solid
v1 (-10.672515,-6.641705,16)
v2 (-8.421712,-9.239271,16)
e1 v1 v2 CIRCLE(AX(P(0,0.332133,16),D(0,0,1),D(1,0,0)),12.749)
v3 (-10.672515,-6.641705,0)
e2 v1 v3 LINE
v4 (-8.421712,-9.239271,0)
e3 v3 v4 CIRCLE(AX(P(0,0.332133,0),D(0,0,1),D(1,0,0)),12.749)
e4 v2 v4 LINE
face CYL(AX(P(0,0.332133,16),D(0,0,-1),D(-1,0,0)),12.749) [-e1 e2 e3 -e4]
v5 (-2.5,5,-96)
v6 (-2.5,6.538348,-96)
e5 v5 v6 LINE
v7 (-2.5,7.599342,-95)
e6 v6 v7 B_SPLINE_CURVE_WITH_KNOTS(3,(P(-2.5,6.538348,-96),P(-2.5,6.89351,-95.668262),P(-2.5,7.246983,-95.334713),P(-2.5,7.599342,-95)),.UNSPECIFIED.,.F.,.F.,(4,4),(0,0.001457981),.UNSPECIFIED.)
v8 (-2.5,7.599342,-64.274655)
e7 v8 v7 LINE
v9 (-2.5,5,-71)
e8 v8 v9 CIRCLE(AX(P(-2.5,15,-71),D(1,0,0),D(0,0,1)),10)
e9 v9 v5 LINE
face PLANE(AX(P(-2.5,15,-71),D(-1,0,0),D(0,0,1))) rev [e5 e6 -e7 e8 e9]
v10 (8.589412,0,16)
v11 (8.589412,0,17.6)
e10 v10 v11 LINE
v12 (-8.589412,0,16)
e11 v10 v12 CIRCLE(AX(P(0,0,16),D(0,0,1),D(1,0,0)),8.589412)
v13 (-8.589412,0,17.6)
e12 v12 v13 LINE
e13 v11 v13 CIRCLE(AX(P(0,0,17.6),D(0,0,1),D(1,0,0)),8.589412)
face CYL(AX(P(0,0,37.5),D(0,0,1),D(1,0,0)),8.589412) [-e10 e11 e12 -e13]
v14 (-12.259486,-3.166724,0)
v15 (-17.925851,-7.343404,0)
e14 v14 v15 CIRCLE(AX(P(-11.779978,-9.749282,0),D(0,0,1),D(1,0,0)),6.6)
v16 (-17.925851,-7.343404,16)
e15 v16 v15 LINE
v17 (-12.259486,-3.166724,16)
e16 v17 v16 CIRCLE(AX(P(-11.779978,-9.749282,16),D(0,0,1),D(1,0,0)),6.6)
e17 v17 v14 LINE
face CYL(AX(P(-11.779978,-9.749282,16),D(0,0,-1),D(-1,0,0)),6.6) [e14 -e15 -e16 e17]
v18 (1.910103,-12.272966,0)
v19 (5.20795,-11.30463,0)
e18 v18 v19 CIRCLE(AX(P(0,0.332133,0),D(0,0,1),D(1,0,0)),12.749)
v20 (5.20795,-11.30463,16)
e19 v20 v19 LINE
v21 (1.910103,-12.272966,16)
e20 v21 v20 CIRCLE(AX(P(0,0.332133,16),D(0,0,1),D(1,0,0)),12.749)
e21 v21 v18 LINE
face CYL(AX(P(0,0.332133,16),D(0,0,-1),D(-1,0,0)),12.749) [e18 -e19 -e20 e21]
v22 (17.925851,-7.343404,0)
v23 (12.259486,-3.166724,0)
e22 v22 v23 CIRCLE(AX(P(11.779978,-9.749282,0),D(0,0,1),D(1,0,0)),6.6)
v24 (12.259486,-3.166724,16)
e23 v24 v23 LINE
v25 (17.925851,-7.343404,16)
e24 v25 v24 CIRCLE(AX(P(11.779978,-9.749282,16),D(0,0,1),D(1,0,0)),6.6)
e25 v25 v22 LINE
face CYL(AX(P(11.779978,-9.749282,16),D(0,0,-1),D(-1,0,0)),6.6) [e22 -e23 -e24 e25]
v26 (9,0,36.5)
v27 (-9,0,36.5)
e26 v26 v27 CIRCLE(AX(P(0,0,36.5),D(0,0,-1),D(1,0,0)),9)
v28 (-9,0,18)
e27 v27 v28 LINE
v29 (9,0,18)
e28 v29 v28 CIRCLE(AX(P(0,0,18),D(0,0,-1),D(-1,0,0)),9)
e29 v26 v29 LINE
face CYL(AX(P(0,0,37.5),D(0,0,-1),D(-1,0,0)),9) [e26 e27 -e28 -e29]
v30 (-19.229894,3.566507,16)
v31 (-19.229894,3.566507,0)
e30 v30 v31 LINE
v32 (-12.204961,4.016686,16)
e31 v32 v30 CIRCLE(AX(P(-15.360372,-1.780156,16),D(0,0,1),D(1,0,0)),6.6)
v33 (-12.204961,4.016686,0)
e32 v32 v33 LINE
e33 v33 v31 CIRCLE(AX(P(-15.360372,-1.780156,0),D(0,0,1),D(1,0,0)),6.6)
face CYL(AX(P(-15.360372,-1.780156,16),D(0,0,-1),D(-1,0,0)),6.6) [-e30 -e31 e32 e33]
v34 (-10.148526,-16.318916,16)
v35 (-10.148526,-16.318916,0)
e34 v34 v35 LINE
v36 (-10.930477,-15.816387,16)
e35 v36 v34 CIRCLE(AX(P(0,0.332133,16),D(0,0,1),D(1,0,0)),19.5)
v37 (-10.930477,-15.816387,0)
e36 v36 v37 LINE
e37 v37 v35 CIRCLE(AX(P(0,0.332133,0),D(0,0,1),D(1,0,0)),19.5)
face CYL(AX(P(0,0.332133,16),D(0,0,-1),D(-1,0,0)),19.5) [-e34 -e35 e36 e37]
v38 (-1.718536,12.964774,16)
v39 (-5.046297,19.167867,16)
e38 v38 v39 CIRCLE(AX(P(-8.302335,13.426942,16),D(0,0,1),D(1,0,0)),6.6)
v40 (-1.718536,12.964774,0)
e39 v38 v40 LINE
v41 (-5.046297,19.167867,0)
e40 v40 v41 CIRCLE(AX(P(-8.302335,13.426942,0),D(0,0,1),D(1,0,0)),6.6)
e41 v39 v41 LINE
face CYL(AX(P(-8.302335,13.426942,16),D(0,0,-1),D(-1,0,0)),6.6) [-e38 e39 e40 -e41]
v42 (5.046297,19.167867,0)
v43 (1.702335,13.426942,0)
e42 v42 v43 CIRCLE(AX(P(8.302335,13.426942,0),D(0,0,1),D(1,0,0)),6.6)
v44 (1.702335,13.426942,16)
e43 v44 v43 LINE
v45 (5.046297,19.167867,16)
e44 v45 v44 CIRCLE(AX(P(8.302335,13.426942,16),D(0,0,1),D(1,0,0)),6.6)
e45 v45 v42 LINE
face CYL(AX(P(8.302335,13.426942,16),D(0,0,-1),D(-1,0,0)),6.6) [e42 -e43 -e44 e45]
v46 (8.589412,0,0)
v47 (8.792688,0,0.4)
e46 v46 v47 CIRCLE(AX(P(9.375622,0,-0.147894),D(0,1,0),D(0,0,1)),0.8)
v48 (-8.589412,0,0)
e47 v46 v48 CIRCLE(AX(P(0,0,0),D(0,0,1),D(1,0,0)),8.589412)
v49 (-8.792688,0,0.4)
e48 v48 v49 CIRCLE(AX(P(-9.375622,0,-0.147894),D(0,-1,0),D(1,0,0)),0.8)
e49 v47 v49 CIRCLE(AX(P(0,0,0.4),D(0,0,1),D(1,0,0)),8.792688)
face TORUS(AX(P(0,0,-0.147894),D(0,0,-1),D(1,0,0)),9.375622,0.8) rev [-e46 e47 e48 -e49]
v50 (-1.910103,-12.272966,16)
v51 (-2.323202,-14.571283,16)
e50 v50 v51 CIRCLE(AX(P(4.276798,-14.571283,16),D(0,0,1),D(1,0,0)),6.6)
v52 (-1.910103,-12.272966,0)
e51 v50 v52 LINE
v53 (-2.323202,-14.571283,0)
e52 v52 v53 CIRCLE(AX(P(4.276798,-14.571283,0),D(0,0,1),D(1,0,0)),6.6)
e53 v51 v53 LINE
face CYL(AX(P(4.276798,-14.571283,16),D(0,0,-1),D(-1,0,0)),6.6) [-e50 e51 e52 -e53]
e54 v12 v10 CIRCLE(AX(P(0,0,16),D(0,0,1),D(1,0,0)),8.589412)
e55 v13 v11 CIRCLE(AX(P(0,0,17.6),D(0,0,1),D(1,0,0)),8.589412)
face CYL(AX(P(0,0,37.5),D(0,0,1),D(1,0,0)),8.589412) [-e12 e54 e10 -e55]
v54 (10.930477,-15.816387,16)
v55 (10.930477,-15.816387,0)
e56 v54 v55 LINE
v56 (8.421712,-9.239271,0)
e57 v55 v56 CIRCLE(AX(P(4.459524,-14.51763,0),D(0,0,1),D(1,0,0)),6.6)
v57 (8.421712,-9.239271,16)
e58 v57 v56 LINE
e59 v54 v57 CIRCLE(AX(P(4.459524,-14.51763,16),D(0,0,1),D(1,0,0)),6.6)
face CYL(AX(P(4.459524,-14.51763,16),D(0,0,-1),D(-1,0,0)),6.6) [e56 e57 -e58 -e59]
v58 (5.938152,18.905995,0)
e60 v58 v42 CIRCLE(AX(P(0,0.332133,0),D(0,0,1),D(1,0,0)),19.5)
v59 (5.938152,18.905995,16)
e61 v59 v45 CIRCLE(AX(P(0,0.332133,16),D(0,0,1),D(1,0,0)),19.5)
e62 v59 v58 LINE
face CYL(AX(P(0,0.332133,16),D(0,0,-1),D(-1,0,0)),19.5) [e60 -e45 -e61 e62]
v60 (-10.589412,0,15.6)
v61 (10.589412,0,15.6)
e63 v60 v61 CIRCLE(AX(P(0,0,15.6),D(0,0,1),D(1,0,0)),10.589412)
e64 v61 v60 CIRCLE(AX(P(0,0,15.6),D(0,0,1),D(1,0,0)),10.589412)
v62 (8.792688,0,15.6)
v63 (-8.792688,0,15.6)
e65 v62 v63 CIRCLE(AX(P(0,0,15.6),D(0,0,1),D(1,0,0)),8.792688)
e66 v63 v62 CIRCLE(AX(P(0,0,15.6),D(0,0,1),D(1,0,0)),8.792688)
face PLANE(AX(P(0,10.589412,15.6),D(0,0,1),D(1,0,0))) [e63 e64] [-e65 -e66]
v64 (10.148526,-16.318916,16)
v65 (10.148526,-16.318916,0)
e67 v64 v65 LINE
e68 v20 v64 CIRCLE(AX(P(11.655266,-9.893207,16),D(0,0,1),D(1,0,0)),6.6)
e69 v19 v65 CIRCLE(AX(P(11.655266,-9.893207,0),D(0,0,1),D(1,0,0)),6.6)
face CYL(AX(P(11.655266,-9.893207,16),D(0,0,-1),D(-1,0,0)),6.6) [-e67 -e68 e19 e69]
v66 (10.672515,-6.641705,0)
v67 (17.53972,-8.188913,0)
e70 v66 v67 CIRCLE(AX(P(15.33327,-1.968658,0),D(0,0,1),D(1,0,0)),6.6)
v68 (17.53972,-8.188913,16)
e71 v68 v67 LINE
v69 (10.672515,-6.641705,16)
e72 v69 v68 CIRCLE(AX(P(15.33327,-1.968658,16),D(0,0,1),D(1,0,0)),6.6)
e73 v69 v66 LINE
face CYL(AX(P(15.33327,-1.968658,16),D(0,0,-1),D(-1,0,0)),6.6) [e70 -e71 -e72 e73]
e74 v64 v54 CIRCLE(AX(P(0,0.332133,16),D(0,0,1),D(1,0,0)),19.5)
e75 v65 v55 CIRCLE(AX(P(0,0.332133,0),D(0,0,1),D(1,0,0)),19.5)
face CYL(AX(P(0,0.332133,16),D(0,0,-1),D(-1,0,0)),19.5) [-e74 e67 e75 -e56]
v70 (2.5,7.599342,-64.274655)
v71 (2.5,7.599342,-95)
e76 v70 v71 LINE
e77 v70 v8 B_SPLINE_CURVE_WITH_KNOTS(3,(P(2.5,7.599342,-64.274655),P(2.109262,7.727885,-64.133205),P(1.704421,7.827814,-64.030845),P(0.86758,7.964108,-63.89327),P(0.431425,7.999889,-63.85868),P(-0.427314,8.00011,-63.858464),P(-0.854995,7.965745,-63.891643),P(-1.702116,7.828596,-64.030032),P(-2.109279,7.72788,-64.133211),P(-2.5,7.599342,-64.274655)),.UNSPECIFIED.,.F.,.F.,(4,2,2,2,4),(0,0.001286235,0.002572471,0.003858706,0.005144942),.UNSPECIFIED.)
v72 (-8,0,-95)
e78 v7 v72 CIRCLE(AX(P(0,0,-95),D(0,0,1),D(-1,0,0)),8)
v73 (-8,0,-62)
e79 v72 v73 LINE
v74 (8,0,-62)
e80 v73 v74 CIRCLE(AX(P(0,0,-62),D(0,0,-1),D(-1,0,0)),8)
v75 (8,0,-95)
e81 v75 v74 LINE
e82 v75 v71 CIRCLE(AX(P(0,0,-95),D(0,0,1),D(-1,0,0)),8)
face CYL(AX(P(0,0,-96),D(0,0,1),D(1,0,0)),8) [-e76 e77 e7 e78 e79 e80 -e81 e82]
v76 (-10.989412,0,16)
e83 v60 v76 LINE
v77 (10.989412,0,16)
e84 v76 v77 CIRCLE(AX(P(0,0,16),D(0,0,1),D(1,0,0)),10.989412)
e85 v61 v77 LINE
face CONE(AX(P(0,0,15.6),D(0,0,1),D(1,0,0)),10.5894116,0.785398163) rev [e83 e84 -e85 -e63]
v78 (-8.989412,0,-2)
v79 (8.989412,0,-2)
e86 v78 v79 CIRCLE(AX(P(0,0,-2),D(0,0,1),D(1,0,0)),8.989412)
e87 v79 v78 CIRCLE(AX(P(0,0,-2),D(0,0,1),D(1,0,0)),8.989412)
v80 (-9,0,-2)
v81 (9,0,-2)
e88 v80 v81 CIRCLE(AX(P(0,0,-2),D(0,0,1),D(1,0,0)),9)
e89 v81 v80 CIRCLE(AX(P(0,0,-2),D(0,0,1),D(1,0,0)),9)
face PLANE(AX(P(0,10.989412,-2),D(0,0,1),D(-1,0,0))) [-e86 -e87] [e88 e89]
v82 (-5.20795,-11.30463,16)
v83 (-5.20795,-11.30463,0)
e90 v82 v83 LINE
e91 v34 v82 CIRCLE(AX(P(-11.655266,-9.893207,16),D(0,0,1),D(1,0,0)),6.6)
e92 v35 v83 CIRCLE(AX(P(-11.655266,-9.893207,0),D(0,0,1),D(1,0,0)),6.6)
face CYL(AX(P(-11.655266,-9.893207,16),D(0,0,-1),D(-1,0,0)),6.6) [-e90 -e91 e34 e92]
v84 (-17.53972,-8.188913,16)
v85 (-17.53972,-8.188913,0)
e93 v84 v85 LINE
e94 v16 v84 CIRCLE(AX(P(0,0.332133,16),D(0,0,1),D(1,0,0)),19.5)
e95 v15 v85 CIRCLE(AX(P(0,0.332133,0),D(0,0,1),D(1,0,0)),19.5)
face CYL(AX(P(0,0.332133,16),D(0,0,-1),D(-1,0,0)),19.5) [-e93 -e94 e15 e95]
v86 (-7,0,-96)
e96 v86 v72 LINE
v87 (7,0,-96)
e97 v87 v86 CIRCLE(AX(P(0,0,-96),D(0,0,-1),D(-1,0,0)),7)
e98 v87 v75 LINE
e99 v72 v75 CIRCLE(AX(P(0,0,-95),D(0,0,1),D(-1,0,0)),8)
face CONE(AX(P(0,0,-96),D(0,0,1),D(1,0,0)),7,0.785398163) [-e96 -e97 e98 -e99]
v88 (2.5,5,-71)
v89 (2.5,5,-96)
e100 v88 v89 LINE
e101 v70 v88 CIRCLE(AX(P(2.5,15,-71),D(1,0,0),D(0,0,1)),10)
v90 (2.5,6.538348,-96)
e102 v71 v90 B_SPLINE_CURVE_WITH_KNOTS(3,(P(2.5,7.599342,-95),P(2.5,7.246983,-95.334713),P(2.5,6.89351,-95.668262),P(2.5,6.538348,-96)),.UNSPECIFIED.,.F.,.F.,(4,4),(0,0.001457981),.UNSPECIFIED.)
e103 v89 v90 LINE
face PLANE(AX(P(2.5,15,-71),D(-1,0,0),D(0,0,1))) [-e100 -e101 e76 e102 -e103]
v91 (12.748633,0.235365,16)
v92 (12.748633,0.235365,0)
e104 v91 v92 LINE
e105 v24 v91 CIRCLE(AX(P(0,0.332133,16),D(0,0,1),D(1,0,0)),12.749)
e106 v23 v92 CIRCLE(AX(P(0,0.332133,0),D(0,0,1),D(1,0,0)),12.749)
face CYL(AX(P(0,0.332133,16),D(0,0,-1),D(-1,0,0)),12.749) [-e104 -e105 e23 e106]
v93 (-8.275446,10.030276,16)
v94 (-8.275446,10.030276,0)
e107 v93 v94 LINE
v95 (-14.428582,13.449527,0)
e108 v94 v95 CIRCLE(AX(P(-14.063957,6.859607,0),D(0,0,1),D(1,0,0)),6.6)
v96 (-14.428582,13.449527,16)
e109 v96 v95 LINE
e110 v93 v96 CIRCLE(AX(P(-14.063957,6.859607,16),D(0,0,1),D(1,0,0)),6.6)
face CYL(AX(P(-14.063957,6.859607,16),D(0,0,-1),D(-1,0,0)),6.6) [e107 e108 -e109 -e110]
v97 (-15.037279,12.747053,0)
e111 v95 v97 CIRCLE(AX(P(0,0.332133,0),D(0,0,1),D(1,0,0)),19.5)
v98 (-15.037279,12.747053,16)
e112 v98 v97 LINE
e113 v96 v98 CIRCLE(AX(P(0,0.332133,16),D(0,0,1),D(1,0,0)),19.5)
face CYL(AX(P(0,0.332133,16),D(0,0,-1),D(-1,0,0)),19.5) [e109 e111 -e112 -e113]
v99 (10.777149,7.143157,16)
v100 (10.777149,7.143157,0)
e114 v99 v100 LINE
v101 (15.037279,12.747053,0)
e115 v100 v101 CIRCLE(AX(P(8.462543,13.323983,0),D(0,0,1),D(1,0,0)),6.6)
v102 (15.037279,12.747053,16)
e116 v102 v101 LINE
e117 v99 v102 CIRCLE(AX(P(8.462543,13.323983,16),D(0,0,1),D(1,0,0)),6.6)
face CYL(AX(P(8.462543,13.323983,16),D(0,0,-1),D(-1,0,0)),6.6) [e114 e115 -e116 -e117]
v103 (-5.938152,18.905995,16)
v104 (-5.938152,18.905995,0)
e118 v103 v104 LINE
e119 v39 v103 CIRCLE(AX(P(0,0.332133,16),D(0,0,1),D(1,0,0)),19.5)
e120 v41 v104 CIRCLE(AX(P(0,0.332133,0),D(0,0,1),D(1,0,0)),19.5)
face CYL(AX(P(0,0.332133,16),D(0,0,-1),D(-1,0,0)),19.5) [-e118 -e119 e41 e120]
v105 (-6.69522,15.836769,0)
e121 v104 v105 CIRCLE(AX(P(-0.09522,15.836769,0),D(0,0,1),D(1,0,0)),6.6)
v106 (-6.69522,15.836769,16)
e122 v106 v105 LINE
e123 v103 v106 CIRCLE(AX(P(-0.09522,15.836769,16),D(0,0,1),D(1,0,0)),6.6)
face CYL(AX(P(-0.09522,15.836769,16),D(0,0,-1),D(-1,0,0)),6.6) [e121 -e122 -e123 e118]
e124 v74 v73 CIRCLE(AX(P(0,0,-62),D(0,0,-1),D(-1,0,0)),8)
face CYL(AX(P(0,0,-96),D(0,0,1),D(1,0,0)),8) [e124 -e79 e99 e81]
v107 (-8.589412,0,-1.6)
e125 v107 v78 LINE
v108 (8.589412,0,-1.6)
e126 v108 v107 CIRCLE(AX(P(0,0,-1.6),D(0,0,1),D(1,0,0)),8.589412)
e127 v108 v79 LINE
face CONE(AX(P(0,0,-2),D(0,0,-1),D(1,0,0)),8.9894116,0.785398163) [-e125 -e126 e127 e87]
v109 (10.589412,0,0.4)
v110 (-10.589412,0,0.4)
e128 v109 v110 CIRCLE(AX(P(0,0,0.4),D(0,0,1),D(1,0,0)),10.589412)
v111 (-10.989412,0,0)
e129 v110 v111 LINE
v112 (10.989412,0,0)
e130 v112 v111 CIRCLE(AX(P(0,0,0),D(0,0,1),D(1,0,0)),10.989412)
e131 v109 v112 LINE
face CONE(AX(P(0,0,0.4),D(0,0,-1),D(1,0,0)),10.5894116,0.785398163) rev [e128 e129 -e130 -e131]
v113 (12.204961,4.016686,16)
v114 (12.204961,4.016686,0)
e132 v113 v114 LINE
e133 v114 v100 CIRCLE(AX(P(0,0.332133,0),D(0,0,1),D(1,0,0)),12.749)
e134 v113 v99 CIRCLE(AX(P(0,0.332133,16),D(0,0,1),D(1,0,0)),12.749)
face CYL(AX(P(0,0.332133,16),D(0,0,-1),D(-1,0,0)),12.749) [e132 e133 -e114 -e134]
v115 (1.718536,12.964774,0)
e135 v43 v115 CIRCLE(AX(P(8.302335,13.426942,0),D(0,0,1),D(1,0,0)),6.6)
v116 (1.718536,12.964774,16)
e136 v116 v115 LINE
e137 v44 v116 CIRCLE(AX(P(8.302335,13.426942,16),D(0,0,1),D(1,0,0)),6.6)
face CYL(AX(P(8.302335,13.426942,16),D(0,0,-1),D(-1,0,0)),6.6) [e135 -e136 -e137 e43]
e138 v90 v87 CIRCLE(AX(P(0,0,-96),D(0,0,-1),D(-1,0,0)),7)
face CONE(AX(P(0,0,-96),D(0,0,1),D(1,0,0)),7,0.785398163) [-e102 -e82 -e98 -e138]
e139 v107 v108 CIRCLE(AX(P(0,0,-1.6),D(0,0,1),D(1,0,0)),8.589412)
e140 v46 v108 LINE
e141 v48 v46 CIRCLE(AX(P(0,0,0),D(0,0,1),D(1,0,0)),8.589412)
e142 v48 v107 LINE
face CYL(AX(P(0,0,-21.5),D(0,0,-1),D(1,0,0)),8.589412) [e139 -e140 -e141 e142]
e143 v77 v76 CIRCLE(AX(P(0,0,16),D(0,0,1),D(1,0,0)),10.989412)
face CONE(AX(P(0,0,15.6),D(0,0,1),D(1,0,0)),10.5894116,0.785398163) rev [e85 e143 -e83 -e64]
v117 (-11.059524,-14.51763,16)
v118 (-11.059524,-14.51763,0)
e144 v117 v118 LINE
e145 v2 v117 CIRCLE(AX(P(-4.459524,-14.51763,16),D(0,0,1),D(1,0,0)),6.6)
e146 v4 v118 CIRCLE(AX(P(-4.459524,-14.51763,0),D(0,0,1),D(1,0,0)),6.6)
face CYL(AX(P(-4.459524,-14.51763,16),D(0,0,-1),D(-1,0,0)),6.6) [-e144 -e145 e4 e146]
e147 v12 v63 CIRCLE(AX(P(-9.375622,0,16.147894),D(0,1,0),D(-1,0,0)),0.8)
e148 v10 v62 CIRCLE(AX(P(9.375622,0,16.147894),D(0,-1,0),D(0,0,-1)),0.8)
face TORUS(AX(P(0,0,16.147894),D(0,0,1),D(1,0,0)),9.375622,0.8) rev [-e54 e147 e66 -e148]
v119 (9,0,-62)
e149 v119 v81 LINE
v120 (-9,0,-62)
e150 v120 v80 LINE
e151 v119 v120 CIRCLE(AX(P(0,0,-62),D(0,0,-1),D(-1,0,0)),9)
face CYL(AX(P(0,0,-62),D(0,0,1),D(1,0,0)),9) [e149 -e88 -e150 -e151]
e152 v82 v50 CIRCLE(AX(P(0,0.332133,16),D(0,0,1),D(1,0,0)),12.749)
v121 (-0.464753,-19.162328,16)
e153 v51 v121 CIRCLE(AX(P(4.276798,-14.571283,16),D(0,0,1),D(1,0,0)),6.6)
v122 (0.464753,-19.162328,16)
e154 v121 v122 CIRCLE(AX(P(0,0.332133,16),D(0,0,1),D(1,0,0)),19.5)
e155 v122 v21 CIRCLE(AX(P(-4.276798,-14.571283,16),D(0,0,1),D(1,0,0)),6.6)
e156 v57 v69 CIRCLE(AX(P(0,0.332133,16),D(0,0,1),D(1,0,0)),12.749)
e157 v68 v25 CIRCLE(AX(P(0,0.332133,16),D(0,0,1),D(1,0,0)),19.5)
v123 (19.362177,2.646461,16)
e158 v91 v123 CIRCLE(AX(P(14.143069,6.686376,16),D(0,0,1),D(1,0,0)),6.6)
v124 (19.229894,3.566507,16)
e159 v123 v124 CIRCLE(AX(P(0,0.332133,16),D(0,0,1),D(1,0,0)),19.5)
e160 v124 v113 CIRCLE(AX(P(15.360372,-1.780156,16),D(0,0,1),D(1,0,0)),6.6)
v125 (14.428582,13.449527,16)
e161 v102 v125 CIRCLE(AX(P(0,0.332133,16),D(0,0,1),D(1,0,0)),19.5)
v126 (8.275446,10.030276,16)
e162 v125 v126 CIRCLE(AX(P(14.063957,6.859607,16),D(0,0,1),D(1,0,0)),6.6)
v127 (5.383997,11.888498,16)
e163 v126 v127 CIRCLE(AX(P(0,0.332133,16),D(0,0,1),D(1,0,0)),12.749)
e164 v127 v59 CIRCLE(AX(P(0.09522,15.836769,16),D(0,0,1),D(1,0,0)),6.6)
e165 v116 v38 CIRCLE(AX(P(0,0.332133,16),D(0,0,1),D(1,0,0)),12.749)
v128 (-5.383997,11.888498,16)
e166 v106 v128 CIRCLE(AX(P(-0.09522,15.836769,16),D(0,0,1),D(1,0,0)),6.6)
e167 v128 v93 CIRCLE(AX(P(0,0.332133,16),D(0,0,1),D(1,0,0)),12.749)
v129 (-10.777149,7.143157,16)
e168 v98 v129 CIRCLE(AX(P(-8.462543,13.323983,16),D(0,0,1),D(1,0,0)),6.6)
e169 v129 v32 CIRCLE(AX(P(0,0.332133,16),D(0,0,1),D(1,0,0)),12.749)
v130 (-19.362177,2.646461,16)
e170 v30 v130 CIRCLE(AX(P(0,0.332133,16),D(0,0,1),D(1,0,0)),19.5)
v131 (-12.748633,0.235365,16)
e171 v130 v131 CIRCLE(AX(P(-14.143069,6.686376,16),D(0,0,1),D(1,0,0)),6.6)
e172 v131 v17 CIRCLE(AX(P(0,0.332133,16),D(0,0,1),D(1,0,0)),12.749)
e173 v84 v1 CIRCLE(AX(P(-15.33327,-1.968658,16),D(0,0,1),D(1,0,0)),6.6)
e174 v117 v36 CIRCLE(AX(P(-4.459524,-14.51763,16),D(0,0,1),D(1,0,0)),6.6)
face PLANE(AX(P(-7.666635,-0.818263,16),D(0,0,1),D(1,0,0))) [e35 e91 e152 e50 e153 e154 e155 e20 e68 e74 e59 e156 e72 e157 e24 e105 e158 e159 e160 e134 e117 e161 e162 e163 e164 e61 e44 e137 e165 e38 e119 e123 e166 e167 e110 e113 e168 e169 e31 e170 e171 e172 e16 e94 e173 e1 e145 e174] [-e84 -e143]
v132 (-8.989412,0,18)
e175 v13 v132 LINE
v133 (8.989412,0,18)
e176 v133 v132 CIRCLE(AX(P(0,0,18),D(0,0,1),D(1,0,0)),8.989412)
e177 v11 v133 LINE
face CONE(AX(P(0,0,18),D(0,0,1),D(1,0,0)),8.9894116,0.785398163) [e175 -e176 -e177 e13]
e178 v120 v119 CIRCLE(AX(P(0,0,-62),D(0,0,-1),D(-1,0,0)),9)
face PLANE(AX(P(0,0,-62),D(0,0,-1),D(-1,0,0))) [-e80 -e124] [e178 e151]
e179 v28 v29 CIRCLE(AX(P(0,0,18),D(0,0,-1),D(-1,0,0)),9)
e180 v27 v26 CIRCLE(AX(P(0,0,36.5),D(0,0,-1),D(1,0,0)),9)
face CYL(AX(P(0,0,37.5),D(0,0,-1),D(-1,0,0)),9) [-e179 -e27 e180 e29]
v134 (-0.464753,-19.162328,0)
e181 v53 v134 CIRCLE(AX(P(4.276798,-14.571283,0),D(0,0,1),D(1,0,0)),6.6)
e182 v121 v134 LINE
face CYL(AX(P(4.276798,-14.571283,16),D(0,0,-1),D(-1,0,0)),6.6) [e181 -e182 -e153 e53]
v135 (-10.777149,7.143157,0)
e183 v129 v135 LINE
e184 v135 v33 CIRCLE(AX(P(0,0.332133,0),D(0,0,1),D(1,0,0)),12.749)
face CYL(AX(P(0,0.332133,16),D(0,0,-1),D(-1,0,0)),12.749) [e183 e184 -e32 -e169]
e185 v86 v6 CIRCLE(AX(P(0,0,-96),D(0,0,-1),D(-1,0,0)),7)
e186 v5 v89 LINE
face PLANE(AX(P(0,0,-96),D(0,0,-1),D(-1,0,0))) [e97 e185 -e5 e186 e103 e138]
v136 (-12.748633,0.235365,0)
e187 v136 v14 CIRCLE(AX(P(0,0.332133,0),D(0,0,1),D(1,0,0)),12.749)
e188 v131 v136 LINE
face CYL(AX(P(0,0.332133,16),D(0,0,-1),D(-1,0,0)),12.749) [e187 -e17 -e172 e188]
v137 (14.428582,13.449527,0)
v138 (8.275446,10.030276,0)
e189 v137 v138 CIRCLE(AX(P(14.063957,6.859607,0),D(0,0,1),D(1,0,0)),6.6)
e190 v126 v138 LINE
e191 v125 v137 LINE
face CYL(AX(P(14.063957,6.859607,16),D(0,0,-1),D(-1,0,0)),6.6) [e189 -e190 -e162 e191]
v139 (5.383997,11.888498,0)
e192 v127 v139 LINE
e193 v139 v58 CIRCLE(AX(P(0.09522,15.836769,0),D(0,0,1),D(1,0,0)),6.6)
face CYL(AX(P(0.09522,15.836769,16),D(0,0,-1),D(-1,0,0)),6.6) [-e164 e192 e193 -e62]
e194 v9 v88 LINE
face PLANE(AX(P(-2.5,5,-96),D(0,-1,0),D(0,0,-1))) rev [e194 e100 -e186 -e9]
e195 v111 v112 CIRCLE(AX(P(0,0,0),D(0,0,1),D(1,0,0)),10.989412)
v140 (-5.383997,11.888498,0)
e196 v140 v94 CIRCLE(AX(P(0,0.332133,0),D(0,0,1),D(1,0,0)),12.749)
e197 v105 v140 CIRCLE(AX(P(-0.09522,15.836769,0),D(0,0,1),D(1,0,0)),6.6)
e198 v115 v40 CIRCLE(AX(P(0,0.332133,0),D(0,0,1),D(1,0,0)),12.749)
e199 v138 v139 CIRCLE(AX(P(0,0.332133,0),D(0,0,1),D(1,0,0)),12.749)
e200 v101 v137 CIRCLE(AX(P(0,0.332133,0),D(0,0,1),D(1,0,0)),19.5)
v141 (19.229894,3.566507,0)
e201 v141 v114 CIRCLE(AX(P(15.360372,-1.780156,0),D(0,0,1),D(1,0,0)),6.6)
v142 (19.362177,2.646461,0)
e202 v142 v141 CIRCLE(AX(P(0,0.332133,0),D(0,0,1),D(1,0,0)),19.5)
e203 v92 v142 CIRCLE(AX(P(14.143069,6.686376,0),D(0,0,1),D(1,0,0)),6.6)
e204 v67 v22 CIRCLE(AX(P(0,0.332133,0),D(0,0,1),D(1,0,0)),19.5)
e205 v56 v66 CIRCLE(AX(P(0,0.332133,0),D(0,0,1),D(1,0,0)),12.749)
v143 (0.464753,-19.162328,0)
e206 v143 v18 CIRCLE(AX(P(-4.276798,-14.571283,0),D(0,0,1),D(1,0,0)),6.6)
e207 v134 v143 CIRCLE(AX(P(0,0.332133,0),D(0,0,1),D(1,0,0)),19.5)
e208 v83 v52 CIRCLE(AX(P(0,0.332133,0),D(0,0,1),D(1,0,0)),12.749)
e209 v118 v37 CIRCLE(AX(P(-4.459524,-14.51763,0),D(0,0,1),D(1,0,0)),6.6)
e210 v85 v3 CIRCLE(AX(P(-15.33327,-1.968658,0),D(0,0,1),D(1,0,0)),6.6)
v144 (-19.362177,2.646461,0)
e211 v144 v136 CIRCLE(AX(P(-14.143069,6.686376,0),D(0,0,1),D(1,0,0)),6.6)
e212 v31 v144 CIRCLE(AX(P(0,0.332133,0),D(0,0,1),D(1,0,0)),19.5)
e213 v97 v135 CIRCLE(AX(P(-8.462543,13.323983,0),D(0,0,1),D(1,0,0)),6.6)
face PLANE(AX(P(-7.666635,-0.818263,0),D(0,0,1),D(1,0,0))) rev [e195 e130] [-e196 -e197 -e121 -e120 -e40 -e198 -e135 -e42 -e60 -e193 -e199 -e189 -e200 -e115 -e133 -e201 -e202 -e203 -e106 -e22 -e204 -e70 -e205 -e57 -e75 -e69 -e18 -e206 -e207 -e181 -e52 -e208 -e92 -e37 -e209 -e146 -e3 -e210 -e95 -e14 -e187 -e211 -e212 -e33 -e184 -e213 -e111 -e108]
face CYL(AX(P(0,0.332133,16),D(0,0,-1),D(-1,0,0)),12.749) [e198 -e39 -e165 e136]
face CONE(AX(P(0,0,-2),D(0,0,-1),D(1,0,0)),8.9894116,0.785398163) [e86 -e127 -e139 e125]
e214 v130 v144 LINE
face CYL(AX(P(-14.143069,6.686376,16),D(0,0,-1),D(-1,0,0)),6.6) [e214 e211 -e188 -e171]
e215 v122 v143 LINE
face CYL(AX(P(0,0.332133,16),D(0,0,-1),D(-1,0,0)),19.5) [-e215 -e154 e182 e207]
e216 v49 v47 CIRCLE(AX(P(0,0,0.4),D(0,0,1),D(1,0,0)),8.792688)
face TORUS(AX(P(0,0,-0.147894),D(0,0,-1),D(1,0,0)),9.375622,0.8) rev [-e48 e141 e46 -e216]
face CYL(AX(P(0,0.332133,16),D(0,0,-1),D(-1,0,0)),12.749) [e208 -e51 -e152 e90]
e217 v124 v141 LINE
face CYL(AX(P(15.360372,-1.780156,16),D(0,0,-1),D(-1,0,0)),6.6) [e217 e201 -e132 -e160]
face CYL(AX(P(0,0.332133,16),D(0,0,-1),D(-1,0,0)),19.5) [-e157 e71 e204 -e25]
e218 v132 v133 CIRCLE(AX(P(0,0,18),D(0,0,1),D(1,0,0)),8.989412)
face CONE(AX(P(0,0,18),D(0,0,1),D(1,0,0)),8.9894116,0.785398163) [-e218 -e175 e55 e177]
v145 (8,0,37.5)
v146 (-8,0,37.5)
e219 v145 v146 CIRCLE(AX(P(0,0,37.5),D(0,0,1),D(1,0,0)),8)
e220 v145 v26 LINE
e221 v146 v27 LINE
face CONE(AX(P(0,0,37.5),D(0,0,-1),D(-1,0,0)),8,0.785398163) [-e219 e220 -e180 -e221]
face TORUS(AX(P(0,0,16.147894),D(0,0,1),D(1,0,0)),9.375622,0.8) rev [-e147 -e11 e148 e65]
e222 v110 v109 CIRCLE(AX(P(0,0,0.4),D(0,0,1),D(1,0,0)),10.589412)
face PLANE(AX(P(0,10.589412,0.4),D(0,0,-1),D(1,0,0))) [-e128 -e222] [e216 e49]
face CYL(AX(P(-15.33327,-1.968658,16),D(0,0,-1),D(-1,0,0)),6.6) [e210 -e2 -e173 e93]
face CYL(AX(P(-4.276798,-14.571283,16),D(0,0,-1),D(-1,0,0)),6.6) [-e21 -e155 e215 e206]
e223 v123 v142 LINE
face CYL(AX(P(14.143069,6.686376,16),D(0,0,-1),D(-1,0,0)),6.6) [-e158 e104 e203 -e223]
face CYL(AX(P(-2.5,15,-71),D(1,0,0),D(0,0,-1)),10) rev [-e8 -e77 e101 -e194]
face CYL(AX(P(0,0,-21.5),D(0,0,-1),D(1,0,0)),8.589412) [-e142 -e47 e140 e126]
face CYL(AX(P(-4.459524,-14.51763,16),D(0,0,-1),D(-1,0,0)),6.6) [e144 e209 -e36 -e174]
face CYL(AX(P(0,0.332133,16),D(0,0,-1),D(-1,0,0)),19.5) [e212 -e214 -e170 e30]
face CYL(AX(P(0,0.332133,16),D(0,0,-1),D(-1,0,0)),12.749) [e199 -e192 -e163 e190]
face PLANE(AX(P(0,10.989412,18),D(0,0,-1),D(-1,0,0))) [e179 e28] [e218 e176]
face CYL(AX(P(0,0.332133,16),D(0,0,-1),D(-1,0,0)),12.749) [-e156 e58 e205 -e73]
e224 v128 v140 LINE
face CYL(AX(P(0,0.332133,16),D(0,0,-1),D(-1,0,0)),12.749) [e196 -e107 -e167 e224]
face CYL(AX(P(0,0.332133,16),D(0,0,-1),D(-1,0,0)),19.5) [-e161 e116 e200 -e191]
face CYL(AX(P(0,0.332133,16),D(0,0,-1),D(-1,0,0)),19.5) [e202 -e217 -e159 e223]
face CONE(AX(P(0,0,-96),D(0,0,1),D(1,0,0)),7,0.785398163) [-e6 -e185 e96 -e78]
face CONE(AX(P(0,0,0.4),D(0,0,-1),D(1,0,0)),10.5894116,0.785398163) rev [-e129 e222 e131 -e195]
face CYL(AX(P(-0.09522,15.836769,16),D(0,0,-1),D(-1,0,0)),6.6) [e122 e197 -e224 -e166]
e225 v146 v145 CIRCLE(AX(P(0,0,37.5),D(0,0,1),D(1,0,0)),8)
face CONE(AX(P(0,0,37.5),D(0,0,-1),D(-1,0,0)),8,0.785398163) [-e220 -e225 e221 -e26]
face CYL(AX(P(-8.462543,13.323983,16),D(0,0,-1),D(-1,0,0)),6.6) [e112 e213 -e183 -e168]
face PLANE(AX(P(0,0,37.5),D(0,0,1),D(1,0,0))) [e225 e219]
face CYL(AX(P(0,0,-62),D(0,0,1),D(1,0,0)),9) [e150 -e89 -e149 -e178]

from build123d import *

# Parameters (mm, degrees)
EXTRUDE_1_DEPTH     = 16
SKETCH_2_R          = 9
EXTRUDE_2_DEPTH     = 21.5
EXTRUDE_START       = 62
SKETCH_3_R          = 9
EXTRUDE_3_DEPTH     = 62
SKETCH_4_R          = 8
EXTRUDE_4_DEPTH     = 34
CUT_EXTRUDE_1_DEPTH = 2.5
CHAMFER_1_SIZE      = 1


with BuildPart() as part:
    # 草图1 → 凸台-拉伸1 (new body)
    with BuildSketch(Plane.XY):
        with BuildLine():
            ThreePointArc((-17.539719795, -8.188913461), (-13.882626521, -8.407262966), (-10.672515451, -6.641705083))
            ThreePointArc((-10.672515451, -6.641705083), (-9.635051323, -8.016686689), (-8.421711588, -9.239271212))
            ThreePointArc((-8.421711588, -9.239271212), (-10.626145075, -12.165442895), (-10.930476691, -15.816386607))
            ThreePointArc((-10.930476691, -15.816386607), (-10.54249594, -16.072311082), (-10.148525822, -16.318915917))
            ThreePointArc((-10.148525822, -16.318915917), (-6.95393453, -14.525429313), (-5.207949909, -11.304630433))
            ThreePointArc((-5.207949909, -11.304630433), (-3.591808367, -11.900443112), (-1.910102932, -12.272965675))
            ThreePointArc((-1.910102932, -12.272965675), (-2.18258254, -15.926424664), (-0.464753394, -19.162328053))
            ThreePointArc((-0.464753394, -19.162328053), (0, -19.167867192), (0.464753394, -19.162328053))
            ThreePointArc((0.464753394, -19.162328053), (2.18258254, -15.926424664), (1.910102932, -12.272965675))
            ThreePointArc((1.910102932, -12.272965675), (3.591808367, -11.900443112), (5.207949909, -11.304630433))
            ThreePointArc((5.207949909, -11.304630433), (6.95393453, -14.525429313), (10.148525822, -16.318915917))
            ThreePointArc((10.148525822, -16.318915917), (10.54249594, -16.072311082), (10.930476691, -15.816386607))
            ThreePointArc((10.930476691, -15.816386607), (10.626145075, -12.165442895), (8.421711588, -9.239271212))
            ThreePointArc((8.421711588, -9.239271212), (9.635051323, -8.016686689), (10.672515451, -6.641705083))
            ThreePointArc((10.672515451, -6.641705083), (13.882626521, -8.407262966), (17.539719795, -8.188913461))
            ThreePointArc((17.539719795, -8.188913461), (17.737823909, -7.768459945), (17.925850869, -7.343404347))
            ThreePointArc((17.925850869, -7.343404347), (15.69598163, -4.436569144), (12.25948632, -3.166723601))
            ThreePointArc((12.25948632, -3.166723601), (12.619233563, -1.482239065), (12.748632746, 0.235364522))
            ThreePointArc((12.748632746, 0.235364522), (16.403682682, 0.485599789), (19.362176663, 2.646460979))
            ThreePointArc((19.362176663, 2.646460979), (19.301518117, 3.107272155), (19.229894055, 3.566506728))
            ThreePointArc((19.229894055, 3.566506728), (15.782454919, 4.806333783), (12.204960767, 4.016686199))
            ThreePointArc((12.204960767, 4.016686199), (11.596898309, 5.628258809), (10.777149222, 7.143157375))
            ThreePointArc((10.777149222, 7.143157375), (13.716685494, 9.329737862), (15.037279247, 12.747052577))
            ThreePointArc((15.037279247, 12.747052577), (14.7371167, 13.10191712), (14.42858175, 13.449526936))
            ThreePointArc((14.42858175, 13.449526936), (10.858110285, 12.628709513), (8.275446406, 10.030276331))
            ThreePointArc((8.275446406, 10.030276331), (6.892629782, 11.057274099), (5.383996967, 11.888498053))
            ThreePointArc((5.383996967, 11.888498053), (6.674737579, 15.317199905), (5.938151919, 18.905994868))
            ThreePointArc((5.938151919, 18.905994868), (5.493784858, 19.042245794), (5.046296687, 19.167867192))
            ThreePointArc((5.046296687, 19.167867192), (2.486392356, 16.547009024), (1.718536283, 12.964774418))
            ThreePointArc((1.718536283, 12.964774418), (0, 13.081132808), (-1.718536283, 12.964774418))
            ThreePointArc((-1.718536283, 12.964774418), (-2.486392356, 16.547009024), (-5.046296687, 19.167867192))
            ThreePointArc((-5.046296687, 19.167867192), (-5.493784858, 19.042245794), (-5.938151919, 18.905994868))
            ThreePointArc((-5.938151919, 18.905994868), (-6.674737579, 15.317199905), (-5.383996967, 11.888498053))
            ThreePointArc((-5.383996967, 11.888498053), (-6.892629782, 11.057274099), (-8.275446406, 10.030276331))
            ThreePointArc((-8.275446406, 10.030276331), (-10.858110285, 12.628709513), (-14.42858175, 13.449526936))
            ThreePointArc((-14.42858175, 13.449526936), (-14.7371167, 13.10191712), (-15.037279247, 12.747052577))
            ThreePointArc((-15.037279247, 12.747052577), (-13.716685494, 9.329737862), (-10.777149222, 7.143157375))
            ThreePointArc((-10.777149222, 7.143157375), (-11.596898309, 5.628258809), (-12.204960767, 4.016686199))
            ThreePointArc((-12.204960767, 4.016686199), (-15.782454919, 4.806333783), (-19.229894055, 3.566506728))
            ThreePointArc((-19.229894055, 3.566506728), (-19.301518117, 3.107272155), (-19.362176663, 2.646460979))
            ThreePointArc((-19.362176663, 2.646460979), (-16.403682682, 0.485599789), (-12.748632746, 0.235364522))
            ThreePointArc((-12.748632746, 0.235364522), (-12.619233563, -1.482239065), (-12.25948632, -3.166723601))
            ThreePointArc((-12.25948632, -3.166723601), (-15.69598163, -4.436569144), (-17.925850869, -7.343404347))
            ThreePointArc((-17.925850869, -7.343404347), (-17.737823909, -7.768459945), (-17.539719795, -8.188913461))
        make_face()
    extrude(amount=EXTRUDE_1_DEPTH)

    # 草图2 → 凸台-拉伸2 (add)
    with BuildSketch(Plane.XY.offset(16)):
        Circle(SKETCH_2_R)
    extrude(amount=EXTRUDE_2_DEPTH)

    # 草图3 → 凸台-拉伸3 (add)
    with BuildSketch(Plane(origin=(0, 0, 0), x_dir=(-1, 0, 0), z_dir=(0, 0, -1)).offset(EXTRUDE_START)):
        with Locations(Location((0, 0, 0), (0, 0, 180))):
            Circle(SKETCH_3_R)
    extrude(amount=-EXTRUDE_3_DEPTH)

    # 草图4 → 凸台-拉伸4 (add)
    with BuildSketch(Plane(origin=(0, 0, -62), x_dir=(-1, 0, 0), z_dir=(0, 0, -1))):
        Circle(SKETCH_4_R)
    extrude(amount=EXTRUDE_4_DEPTH)

    # 草图5 → 切除-旋转1 (revolve, cut)
    with BuildSketch(Plane(origin=(0, 0, 0), x_dir=(0, 0, -1), z_dir=(1, 0, 0)), mode=Mode.PRIVATE) as cut_revolve_1_sk:
        with BuildLine():
            Line((-16, 10.9894116), (-15.6, 10.5894116))
            Line((-15.6, 10.5894116), (-15.6, 8.792688481))
            ThreePointArc((-15.6, 8.792688481), (-15.785456972, 8.662432859), (-16, 8.5894116))
            Line((-16, 8.5894116), (-17.6, 8.5894116))
            Line((-17.6, 8.5894116), (-18, 8.9894116))
            Line((-18, 8.9894116), (-18, 10.9894116))
            Line((-18, 10.9894116), (-16, 10.9894116))
        make_face()
    cut_revolve_1 = revolve(cut_revolve_1_sk.sketch.rotate(Axis((0, 0, 37.5), (0, 0, -1)), 90), axis=Axis((0, 0, 37.5), (0, 0, -1)), mode=Mode.SUBTRACT)

    # 镜向1: 切除-旋转1 across plane
    add(cut_revolve_1.mirror(Plane.XY.offset(8)), mode=Mode.SUBTRACT)

    # 草图6 → 切除-拉伸1 (cut, symmetric)
    with BuildSketch(Plane(origin=(0, 0, 0), x_dir=(0, 0, -1), z_dir=(1, 0, 0))):
        with BuildLine():
            Line((96, 12.940111189), (96, 5))
            Line((96, 5), (71, 5))
            ThreePointArc((71, 5), (64.570358548, 7.341037224), (61.151123092, 13.268057839))
            Line((61.151123092, 13.268057839), (61.151123092, 20.241558611))
            Line((61.151123092, 20.241558611), (96, 20.241558611))
            Line((96, 20.241558611), (96, 12.940111189))
        make_face()
    extrude(amount=CUT_EXTRUDE_1_DEPTH, both=True, mode=Mode.SUBTRACT)

    # 倒角1
    chamfer_1_edges = [part.edges().sort_by_distance(p)[0] for p in [
        (-9, 0, 37.5),
        (4.69041576, -6.480740698, -96),
    ]]
    chamfer(chamfer_1_edges, length=CHAMFER_1_SIZE)


solid = part.part
